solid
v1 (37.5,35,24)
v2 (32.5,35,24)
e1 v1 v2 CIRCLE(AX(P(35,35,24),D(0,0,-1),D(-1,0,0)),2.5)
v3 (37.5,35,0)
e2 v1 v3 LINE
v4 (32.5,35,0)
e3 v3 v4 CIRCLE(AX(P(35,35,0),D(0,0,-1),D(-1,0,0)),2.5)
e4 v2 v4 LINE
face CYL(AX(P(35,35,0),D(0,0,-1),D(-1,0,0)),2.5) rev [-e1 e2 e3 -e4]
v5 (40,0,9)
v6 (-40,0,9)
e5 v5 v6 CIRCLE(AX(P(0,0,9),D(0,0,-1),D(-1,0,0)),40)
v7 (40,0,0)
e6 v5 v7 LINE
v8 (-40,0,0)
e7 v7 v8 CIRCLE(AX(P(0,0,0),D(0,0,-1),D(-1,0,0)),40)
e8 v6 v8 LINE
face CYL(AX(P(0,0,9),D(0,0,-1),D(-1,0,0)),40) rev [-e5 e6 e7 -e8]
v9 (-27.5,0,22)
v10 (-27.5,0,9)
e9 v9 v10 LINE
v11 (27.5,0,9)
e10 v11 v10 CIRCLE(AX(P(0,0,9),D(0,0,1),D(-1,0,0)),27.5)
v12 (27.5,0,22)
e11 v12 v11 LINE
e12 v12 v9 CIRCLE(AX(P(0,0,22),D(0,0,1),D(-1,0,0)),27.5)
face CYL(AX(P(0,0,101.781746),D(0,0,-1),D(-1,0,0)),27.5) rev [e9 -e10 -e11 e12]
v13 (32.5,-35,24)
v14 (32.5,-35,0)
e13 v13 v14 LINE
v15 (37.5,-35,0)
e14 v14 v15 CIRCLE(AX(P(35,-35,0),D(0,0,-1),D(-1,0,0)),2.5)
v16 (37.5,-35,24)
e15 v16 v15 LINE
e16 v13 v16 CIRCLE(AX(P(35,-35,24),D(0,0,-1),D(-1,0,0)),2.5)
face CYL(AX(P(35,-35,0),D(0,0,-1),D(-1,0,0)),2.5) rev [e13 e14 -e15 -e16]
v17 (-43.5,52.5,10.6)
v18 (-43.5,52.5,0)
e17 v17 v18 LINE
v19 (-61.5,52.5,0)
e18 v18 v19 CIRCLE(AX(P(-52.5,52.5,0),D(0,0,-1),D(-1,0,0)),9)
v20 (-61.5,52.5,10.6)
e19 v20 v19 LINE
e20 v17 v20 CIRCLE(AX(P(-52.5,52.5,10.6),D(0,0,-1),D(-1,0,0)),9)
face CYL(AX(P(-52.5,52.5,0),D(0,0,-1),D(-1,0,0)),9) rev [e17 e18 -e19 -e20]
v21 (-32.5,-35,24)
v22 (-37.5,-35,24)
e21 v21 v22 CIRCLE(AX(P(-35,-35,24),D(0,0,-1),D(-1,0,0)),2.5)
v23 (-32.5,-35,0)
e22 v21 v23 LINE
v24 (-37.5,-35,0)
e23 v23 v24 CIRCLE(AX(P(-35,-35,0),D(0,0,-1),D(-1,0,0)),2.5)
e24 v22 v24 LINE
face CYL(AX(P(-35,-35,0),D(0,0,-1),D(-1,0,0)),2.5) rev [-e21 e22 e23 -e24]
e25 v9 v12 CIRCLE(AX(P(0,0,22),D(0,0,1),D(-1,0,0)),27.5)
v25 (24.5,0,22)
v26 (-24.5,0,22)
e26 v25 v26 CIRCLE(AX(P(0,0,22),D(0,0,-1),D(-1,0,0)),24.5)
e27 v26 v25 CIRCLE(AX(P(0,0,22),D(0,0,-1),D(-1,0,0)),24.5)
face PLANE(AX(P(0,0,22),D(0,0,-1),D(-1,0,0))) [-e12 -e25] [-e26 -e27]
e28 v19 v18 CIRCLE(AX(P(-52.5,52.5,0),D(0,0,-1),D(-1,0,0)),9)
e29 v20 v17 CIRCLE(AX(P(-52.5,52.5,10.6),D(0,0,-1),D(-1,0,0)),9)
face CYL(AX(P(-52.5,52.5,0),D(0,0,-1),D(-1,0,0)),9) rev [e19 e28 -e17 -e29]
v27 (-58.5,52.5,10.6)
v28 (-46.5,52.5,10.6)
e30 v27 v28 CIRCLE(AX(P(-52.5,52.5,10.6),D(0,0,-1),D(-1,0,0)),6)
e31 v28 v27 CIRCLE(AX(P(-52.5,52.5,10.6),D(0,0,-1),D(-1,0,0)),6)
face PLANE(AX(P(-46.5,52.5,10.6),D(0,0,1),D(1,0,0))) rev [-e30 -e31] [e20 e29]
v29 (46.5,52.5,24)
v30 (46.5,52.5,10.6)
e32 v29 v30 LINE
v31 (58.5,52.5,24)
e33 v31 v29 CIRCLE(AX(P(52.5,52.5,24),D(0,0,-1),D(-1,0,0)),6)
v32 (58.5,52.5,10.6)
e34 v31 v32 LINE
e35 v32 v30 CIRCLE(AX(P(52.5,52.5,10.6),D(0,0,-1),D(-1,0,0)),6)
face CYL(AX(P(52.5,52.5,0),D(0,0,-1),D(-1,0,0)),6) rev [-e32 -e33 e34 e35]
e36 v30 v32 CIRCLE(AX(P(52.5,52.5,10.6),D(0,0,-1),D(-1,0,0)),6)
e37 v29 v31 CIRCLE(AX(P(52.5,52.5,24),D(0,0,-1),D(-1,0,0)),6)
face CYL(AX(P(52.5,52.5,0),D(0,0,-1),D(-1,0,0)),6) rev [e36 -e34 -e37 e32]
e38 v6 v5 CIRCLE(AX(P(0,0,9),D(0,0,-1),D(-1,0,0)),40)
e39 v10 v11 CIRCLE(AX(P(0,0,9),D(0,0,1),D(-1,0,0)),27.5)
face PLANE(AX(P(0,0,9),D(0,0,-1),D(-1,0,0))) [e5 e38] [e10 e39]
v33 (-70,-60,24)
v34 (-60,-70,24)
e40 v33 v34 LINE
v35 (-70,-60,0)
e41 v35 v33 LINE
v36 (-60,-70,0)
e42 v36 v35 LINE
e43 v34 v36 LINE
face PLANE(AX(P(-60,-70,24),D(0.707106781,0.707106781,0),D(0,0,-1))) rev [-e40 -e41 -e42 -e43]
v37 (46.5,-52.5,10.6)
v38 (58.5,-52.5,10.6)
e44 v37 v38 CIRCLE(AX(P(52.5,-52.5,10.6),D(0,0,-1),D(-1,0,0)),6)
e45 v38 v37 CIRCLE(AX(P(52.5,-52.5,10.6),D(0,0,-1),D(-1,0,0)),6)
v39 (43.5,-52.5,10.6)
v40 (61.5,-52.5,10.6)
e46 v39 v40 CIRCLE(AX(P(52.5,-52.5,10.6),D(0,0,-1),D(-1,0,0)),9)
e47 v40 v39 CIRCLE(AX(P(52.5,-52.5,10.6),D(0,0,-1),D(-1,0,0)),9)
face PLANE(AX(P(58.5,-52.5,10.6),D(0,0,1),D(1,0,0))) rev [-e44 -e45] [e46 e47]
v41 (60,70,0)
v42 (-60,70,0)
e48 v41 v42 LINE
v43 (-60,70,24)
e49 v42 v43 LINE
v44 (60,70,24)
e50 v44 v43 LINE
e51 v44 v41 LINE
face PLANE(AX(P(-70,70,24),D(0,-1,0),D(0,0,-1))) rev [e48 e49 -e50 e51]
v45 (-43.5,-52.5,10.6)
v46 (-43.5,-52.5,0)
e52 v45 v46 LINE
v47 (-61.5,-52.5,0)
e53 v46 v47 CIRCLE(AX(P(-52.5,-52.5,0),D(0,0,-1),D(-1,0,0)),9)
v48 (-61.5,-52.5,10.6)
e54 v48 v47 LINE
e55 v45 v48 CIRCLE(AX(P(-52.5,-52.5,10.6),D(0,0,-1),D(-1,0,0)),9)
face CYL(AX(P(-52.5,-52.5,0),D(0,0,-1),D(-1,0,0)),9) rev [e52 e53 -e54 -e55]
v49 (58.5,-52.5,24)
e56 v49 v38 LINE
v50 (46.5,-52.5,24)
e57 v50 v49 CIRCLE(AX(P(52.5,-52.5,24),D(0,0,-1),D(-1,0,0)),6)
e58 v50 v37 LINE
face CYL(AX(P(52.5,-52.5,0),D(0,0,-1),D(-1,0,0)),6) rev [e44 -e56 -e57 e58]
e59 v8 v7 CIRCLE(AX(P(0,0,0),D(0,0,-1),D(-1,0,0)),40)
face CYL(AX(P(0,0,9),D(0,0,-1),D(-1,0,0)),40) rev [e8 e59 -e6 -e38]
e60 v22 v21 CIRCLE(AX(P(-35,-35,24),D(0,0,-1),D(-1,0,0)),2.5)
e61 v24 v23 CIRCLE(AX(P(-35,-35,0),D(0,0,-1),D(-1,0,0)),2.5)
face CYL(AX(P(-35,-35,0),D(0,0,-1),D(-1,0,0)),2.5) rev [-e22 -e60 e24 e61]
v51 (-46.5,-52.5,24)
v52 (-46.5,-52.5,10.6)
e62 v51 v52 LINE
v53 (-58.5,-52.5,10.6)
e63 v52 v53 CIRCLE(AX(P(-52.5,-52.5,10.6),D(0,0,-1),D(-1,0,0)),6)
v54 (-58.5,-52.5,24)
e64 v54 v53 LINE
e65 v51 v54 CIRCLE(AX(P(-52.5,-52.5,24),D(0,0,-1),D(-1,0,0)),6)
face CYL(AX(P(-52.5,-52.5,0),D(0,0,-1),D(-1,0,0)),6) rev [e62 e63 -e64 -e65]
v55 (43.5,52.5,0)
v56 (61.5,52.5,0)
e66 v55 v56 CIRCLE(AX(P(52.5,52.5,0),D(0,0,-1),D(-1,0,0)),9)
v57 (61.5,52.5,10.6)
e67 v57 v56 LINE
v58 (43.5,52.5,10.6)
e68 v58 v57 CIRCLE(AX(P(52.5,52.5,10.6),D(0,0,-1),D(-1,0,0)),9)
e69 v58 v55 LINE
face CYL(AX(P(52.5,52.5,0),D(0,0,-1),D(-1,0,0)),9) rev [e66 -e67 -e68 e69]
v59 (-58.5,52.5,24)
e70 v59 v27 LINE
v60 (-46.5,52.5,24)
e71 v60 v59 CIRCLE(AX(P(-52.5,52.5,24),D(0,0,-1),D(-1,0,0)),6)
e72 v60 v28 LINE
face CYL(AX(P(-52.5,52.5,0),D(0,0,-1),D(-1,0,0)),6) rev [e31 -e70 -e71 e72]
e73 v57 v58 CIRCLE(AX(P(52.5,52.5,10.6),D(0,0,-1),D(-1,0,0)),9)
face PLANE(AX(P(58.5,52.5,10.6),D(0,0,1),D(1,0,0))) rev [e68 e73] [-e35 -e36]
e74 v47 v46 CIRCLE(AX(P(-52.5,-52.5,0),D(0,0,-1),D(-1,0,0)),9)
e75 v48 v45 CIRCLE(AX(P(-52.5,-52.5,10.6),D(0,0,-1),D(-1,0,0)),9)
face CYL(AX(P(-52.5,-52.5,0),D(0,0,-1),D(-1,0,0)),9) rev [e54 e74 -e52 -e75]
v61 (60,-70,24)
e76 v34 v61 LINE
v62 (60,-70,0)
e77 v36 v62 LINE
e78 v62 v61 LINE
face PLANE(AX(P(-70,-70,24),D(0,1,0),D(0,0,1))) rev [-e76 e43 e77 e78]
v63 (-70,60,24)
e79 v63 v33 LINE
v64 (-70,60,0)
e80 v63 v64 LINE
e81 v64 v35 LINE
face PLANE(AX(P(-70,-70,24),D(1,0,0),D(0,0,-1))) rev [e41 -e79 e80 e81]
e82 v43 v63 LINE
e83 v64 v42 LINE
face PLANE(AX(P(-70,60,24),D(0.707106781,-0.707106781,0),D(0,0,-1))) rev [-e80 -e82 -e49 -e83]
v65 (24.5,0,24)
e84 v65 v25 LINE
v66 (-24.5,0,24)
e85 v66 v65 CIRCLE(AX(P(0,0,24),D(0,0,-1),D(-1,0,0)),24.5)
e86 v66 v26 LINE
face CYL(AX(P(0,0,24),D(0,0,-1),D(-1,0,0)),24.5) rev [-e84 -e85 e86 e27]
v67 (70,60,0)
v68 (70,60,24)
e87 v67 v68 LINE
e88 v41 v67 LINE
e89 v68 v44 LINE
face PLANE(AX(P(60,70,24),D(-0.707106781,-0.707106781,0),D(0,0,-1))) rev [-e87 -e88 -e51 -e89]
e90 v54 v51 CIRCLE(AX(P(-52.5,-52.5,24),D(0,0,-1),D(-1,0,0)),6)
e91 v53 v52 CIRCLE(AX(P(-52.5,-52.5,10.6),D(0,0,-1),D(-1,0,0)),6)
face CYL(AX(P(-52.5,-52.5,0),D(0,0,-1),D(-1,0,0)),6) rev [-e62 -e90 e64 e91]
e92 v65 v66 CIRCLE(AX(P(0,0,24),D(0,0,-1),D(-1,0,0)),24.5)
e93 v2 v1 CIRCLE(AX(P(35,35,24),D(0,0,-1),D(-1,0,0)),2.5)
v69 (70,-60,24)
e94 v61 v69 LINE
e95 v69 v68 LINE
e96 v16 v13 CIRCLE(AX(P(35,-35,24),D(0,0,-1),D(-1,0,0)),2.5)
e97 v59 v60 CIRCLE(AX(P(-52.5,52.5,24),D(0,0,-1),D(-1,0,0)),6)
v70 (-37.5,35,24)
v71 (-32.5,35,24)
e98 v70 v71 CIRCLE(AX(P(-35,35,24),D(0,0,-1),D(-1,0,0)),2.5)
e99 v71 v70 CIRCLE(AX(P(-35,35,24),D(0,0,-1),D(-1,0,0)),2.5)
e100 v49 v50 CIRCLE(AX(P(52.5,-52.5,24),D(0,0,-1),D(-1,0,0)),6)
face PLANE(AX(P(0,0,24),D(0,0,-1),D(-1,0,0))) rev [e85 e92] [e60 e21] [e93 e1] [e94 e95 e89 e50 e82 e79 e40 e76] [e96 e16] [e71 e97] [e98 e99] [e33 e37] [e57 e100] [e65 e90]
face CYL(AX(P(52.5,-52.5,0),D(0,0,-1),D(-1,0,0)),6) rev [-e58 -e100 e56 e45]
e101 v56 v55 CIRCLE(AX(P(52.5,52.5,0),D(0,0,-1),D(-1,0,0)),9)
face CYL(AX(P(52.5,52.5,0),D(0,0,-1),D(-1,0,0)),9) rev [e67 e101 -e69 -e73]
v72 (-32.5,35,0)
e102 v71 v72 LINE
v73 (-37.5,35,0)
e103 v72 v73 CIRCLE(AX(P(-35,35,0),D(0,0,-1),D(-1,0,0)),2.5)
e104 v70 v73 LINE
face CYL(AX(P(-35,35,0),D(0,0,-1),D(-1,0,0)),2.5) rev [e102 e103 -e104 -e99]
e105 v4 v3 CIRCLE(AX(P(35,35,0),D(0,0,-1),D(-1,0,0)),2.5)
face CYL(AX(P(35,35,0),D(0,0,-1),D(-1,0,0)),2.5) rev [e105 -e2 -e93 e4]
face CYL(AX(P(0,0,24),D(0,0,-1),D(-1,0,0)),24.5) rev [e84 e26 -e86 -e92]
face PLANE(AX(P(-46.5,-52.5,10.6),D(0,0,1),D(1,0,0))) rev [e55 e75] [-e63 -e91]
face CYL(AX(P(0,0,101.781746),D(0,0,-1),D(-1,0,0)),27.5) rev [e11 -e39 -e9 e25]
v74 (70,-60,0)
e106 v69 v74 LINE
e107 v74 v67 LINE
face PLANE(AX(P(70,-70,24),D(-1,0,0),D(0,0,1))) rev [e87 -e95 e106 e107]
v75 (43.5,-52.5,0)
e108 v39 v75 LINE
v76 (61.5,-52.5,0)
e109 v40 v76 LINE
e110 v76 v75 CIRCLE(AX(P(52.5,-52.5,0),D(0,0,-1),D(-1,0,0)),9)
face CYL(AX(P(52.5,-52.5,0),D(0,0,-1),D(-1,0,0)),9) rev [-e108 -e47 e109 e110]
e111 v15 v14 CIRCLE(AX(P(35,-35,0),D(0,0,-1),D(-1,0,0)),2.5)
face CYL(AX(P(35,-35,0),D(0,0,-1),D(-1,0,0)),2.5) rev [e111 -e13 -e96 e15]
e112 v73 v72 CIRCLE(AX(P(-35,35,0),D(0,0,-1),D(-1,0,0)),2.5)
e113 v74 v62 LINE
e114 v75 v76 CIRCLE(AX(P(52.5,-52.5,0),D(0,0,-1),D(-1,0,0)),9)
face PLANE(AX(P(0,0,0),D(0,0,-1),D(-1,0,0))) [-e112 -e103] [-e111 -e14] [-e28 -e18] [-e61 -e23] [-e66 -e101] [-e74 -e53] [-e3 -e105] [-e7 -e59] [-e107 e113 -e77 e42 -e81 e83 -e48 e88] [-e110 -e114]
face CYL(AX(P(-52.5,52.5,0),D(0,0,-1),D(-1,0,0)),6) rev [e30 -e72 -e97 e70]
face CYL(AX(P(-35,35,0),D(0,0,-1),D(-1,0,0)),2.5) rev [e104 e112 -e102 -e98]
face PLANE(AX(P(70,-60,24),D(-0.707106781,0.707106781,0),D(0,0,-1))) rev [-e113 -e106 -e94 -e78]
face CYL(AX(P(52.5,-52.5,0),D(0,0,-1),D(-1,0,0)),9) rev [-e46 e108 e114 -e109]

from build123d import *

# Parameters (mm, degrees)
SKETCH_1_W                    = 140
SKETCH_1_H                    = 140
EXTRUDE_1_DEPTH               = 24
SKETCH_2_R                    = 27.5
CUT_EXTRUDE_1_DEPTH           = 22
SKETCH_3_R                    = 24.5
CUT_EXTRUDE_2_DEPTH           = 102.410058673
HOLE_WIZARD_M10_1_D           = 12
HOLE_WIZARD_M10_1_CBORE_D     = 18
HOLE_WIZARD_M10_1_CBORE_DEPTH = 10.6
CHAMFER_1_SIZE                = 10
HOLE_WIZARD_M6_1_D            = 5
SKETCH_11_R                   = 40
CUT_EXTRUDE_3_DEPTH           = 9


with BuildPart() as part:
    # 草图1 → 凸台-拉伸1 (new body)
    with BuildSketch(Plane.XY):
        Rectangle(SKETCH_1_W, SKETCH_1_H)
    extrude(amount=EXTRUDE_1_DEPTH)

    # 草图2 → 切除-拉伸1 (cut)
    with BuildSketch(Plane(origin=(0, 0, 0), x_dir=(-1, 0, 0), z_dir=(0, 0, -1))):
        Circle(SKETCH_2_R)
    extrude(amount=-CUT_EXTRUDE_1_DEPTH, mode=Mode.SUBTRACT)

    # 草图3 → 切除-拉伸2 (cut, through all)
    with BuildSketch(Plane(origin=(0, 0, 22), x_dir=(-1, 0, 0), z_dir=(0, 0, -1))):
        Circle(SKETCH_3_R)
    extrude(amount=-CUT_EXTRUDE_2_DEPTH, mode=Mode.SUBTRACT)

    # M10 六角凹头螺钉的柱形沉头孔1 (through all)
    with Locations(Plane(origin=(0, 0, 0), x_dir=(-1, 0, 0), z_dir=(0, 0, -1))):
        with Locations((-52.5, 52.5), (52.5, 52.5), (52.5, -52.5), (-52.5, -52.5)):
            CounterBoreHole(HOLE_WIZARD_M10_1_D / 2, HOLE_WIZARD_M10_1_CBORE_D / 2, HOLE_WIZARD_M10_1_CBORE_DEPTH)

    # 倒角1
    chamfer_1_edges = [part.edges().sort_by_distance(p)[0] for p in [
        (70, -70, 12),
        (-70, -70, 12),
        (-70, 70, 12),
        (70, 70, 12),
    ]]
    chamfer(chamfer_1_edges, length=CHAMFER_1_SIZE)

    # M6 螺纹孔1 (through all)
    with Locations(Plane(origin=(0, 0, 0), x_dir=(-1, 0, 0), z_dir=(0, 0, -1))):
        with Locations((-35, 35), (35, 35), (35, -35), (-35, -35), (0, 0)):
            Hole(HOLE_WIZARD_M6_1_D / 2)

    # 草图11 → 切除-拉伸3 (cut)
    with BuildSketch(Plane(origin=(0, 0, 0), x_dir=(-1, 0, 0), z_dir=(0, 0, -1))):
        Circle(SKETCH_11_R)
    extrude(amount=-CUT_EXTRUDE_3_DEPTH, mode=Mode.SUBTRACT)


solid = part.part
